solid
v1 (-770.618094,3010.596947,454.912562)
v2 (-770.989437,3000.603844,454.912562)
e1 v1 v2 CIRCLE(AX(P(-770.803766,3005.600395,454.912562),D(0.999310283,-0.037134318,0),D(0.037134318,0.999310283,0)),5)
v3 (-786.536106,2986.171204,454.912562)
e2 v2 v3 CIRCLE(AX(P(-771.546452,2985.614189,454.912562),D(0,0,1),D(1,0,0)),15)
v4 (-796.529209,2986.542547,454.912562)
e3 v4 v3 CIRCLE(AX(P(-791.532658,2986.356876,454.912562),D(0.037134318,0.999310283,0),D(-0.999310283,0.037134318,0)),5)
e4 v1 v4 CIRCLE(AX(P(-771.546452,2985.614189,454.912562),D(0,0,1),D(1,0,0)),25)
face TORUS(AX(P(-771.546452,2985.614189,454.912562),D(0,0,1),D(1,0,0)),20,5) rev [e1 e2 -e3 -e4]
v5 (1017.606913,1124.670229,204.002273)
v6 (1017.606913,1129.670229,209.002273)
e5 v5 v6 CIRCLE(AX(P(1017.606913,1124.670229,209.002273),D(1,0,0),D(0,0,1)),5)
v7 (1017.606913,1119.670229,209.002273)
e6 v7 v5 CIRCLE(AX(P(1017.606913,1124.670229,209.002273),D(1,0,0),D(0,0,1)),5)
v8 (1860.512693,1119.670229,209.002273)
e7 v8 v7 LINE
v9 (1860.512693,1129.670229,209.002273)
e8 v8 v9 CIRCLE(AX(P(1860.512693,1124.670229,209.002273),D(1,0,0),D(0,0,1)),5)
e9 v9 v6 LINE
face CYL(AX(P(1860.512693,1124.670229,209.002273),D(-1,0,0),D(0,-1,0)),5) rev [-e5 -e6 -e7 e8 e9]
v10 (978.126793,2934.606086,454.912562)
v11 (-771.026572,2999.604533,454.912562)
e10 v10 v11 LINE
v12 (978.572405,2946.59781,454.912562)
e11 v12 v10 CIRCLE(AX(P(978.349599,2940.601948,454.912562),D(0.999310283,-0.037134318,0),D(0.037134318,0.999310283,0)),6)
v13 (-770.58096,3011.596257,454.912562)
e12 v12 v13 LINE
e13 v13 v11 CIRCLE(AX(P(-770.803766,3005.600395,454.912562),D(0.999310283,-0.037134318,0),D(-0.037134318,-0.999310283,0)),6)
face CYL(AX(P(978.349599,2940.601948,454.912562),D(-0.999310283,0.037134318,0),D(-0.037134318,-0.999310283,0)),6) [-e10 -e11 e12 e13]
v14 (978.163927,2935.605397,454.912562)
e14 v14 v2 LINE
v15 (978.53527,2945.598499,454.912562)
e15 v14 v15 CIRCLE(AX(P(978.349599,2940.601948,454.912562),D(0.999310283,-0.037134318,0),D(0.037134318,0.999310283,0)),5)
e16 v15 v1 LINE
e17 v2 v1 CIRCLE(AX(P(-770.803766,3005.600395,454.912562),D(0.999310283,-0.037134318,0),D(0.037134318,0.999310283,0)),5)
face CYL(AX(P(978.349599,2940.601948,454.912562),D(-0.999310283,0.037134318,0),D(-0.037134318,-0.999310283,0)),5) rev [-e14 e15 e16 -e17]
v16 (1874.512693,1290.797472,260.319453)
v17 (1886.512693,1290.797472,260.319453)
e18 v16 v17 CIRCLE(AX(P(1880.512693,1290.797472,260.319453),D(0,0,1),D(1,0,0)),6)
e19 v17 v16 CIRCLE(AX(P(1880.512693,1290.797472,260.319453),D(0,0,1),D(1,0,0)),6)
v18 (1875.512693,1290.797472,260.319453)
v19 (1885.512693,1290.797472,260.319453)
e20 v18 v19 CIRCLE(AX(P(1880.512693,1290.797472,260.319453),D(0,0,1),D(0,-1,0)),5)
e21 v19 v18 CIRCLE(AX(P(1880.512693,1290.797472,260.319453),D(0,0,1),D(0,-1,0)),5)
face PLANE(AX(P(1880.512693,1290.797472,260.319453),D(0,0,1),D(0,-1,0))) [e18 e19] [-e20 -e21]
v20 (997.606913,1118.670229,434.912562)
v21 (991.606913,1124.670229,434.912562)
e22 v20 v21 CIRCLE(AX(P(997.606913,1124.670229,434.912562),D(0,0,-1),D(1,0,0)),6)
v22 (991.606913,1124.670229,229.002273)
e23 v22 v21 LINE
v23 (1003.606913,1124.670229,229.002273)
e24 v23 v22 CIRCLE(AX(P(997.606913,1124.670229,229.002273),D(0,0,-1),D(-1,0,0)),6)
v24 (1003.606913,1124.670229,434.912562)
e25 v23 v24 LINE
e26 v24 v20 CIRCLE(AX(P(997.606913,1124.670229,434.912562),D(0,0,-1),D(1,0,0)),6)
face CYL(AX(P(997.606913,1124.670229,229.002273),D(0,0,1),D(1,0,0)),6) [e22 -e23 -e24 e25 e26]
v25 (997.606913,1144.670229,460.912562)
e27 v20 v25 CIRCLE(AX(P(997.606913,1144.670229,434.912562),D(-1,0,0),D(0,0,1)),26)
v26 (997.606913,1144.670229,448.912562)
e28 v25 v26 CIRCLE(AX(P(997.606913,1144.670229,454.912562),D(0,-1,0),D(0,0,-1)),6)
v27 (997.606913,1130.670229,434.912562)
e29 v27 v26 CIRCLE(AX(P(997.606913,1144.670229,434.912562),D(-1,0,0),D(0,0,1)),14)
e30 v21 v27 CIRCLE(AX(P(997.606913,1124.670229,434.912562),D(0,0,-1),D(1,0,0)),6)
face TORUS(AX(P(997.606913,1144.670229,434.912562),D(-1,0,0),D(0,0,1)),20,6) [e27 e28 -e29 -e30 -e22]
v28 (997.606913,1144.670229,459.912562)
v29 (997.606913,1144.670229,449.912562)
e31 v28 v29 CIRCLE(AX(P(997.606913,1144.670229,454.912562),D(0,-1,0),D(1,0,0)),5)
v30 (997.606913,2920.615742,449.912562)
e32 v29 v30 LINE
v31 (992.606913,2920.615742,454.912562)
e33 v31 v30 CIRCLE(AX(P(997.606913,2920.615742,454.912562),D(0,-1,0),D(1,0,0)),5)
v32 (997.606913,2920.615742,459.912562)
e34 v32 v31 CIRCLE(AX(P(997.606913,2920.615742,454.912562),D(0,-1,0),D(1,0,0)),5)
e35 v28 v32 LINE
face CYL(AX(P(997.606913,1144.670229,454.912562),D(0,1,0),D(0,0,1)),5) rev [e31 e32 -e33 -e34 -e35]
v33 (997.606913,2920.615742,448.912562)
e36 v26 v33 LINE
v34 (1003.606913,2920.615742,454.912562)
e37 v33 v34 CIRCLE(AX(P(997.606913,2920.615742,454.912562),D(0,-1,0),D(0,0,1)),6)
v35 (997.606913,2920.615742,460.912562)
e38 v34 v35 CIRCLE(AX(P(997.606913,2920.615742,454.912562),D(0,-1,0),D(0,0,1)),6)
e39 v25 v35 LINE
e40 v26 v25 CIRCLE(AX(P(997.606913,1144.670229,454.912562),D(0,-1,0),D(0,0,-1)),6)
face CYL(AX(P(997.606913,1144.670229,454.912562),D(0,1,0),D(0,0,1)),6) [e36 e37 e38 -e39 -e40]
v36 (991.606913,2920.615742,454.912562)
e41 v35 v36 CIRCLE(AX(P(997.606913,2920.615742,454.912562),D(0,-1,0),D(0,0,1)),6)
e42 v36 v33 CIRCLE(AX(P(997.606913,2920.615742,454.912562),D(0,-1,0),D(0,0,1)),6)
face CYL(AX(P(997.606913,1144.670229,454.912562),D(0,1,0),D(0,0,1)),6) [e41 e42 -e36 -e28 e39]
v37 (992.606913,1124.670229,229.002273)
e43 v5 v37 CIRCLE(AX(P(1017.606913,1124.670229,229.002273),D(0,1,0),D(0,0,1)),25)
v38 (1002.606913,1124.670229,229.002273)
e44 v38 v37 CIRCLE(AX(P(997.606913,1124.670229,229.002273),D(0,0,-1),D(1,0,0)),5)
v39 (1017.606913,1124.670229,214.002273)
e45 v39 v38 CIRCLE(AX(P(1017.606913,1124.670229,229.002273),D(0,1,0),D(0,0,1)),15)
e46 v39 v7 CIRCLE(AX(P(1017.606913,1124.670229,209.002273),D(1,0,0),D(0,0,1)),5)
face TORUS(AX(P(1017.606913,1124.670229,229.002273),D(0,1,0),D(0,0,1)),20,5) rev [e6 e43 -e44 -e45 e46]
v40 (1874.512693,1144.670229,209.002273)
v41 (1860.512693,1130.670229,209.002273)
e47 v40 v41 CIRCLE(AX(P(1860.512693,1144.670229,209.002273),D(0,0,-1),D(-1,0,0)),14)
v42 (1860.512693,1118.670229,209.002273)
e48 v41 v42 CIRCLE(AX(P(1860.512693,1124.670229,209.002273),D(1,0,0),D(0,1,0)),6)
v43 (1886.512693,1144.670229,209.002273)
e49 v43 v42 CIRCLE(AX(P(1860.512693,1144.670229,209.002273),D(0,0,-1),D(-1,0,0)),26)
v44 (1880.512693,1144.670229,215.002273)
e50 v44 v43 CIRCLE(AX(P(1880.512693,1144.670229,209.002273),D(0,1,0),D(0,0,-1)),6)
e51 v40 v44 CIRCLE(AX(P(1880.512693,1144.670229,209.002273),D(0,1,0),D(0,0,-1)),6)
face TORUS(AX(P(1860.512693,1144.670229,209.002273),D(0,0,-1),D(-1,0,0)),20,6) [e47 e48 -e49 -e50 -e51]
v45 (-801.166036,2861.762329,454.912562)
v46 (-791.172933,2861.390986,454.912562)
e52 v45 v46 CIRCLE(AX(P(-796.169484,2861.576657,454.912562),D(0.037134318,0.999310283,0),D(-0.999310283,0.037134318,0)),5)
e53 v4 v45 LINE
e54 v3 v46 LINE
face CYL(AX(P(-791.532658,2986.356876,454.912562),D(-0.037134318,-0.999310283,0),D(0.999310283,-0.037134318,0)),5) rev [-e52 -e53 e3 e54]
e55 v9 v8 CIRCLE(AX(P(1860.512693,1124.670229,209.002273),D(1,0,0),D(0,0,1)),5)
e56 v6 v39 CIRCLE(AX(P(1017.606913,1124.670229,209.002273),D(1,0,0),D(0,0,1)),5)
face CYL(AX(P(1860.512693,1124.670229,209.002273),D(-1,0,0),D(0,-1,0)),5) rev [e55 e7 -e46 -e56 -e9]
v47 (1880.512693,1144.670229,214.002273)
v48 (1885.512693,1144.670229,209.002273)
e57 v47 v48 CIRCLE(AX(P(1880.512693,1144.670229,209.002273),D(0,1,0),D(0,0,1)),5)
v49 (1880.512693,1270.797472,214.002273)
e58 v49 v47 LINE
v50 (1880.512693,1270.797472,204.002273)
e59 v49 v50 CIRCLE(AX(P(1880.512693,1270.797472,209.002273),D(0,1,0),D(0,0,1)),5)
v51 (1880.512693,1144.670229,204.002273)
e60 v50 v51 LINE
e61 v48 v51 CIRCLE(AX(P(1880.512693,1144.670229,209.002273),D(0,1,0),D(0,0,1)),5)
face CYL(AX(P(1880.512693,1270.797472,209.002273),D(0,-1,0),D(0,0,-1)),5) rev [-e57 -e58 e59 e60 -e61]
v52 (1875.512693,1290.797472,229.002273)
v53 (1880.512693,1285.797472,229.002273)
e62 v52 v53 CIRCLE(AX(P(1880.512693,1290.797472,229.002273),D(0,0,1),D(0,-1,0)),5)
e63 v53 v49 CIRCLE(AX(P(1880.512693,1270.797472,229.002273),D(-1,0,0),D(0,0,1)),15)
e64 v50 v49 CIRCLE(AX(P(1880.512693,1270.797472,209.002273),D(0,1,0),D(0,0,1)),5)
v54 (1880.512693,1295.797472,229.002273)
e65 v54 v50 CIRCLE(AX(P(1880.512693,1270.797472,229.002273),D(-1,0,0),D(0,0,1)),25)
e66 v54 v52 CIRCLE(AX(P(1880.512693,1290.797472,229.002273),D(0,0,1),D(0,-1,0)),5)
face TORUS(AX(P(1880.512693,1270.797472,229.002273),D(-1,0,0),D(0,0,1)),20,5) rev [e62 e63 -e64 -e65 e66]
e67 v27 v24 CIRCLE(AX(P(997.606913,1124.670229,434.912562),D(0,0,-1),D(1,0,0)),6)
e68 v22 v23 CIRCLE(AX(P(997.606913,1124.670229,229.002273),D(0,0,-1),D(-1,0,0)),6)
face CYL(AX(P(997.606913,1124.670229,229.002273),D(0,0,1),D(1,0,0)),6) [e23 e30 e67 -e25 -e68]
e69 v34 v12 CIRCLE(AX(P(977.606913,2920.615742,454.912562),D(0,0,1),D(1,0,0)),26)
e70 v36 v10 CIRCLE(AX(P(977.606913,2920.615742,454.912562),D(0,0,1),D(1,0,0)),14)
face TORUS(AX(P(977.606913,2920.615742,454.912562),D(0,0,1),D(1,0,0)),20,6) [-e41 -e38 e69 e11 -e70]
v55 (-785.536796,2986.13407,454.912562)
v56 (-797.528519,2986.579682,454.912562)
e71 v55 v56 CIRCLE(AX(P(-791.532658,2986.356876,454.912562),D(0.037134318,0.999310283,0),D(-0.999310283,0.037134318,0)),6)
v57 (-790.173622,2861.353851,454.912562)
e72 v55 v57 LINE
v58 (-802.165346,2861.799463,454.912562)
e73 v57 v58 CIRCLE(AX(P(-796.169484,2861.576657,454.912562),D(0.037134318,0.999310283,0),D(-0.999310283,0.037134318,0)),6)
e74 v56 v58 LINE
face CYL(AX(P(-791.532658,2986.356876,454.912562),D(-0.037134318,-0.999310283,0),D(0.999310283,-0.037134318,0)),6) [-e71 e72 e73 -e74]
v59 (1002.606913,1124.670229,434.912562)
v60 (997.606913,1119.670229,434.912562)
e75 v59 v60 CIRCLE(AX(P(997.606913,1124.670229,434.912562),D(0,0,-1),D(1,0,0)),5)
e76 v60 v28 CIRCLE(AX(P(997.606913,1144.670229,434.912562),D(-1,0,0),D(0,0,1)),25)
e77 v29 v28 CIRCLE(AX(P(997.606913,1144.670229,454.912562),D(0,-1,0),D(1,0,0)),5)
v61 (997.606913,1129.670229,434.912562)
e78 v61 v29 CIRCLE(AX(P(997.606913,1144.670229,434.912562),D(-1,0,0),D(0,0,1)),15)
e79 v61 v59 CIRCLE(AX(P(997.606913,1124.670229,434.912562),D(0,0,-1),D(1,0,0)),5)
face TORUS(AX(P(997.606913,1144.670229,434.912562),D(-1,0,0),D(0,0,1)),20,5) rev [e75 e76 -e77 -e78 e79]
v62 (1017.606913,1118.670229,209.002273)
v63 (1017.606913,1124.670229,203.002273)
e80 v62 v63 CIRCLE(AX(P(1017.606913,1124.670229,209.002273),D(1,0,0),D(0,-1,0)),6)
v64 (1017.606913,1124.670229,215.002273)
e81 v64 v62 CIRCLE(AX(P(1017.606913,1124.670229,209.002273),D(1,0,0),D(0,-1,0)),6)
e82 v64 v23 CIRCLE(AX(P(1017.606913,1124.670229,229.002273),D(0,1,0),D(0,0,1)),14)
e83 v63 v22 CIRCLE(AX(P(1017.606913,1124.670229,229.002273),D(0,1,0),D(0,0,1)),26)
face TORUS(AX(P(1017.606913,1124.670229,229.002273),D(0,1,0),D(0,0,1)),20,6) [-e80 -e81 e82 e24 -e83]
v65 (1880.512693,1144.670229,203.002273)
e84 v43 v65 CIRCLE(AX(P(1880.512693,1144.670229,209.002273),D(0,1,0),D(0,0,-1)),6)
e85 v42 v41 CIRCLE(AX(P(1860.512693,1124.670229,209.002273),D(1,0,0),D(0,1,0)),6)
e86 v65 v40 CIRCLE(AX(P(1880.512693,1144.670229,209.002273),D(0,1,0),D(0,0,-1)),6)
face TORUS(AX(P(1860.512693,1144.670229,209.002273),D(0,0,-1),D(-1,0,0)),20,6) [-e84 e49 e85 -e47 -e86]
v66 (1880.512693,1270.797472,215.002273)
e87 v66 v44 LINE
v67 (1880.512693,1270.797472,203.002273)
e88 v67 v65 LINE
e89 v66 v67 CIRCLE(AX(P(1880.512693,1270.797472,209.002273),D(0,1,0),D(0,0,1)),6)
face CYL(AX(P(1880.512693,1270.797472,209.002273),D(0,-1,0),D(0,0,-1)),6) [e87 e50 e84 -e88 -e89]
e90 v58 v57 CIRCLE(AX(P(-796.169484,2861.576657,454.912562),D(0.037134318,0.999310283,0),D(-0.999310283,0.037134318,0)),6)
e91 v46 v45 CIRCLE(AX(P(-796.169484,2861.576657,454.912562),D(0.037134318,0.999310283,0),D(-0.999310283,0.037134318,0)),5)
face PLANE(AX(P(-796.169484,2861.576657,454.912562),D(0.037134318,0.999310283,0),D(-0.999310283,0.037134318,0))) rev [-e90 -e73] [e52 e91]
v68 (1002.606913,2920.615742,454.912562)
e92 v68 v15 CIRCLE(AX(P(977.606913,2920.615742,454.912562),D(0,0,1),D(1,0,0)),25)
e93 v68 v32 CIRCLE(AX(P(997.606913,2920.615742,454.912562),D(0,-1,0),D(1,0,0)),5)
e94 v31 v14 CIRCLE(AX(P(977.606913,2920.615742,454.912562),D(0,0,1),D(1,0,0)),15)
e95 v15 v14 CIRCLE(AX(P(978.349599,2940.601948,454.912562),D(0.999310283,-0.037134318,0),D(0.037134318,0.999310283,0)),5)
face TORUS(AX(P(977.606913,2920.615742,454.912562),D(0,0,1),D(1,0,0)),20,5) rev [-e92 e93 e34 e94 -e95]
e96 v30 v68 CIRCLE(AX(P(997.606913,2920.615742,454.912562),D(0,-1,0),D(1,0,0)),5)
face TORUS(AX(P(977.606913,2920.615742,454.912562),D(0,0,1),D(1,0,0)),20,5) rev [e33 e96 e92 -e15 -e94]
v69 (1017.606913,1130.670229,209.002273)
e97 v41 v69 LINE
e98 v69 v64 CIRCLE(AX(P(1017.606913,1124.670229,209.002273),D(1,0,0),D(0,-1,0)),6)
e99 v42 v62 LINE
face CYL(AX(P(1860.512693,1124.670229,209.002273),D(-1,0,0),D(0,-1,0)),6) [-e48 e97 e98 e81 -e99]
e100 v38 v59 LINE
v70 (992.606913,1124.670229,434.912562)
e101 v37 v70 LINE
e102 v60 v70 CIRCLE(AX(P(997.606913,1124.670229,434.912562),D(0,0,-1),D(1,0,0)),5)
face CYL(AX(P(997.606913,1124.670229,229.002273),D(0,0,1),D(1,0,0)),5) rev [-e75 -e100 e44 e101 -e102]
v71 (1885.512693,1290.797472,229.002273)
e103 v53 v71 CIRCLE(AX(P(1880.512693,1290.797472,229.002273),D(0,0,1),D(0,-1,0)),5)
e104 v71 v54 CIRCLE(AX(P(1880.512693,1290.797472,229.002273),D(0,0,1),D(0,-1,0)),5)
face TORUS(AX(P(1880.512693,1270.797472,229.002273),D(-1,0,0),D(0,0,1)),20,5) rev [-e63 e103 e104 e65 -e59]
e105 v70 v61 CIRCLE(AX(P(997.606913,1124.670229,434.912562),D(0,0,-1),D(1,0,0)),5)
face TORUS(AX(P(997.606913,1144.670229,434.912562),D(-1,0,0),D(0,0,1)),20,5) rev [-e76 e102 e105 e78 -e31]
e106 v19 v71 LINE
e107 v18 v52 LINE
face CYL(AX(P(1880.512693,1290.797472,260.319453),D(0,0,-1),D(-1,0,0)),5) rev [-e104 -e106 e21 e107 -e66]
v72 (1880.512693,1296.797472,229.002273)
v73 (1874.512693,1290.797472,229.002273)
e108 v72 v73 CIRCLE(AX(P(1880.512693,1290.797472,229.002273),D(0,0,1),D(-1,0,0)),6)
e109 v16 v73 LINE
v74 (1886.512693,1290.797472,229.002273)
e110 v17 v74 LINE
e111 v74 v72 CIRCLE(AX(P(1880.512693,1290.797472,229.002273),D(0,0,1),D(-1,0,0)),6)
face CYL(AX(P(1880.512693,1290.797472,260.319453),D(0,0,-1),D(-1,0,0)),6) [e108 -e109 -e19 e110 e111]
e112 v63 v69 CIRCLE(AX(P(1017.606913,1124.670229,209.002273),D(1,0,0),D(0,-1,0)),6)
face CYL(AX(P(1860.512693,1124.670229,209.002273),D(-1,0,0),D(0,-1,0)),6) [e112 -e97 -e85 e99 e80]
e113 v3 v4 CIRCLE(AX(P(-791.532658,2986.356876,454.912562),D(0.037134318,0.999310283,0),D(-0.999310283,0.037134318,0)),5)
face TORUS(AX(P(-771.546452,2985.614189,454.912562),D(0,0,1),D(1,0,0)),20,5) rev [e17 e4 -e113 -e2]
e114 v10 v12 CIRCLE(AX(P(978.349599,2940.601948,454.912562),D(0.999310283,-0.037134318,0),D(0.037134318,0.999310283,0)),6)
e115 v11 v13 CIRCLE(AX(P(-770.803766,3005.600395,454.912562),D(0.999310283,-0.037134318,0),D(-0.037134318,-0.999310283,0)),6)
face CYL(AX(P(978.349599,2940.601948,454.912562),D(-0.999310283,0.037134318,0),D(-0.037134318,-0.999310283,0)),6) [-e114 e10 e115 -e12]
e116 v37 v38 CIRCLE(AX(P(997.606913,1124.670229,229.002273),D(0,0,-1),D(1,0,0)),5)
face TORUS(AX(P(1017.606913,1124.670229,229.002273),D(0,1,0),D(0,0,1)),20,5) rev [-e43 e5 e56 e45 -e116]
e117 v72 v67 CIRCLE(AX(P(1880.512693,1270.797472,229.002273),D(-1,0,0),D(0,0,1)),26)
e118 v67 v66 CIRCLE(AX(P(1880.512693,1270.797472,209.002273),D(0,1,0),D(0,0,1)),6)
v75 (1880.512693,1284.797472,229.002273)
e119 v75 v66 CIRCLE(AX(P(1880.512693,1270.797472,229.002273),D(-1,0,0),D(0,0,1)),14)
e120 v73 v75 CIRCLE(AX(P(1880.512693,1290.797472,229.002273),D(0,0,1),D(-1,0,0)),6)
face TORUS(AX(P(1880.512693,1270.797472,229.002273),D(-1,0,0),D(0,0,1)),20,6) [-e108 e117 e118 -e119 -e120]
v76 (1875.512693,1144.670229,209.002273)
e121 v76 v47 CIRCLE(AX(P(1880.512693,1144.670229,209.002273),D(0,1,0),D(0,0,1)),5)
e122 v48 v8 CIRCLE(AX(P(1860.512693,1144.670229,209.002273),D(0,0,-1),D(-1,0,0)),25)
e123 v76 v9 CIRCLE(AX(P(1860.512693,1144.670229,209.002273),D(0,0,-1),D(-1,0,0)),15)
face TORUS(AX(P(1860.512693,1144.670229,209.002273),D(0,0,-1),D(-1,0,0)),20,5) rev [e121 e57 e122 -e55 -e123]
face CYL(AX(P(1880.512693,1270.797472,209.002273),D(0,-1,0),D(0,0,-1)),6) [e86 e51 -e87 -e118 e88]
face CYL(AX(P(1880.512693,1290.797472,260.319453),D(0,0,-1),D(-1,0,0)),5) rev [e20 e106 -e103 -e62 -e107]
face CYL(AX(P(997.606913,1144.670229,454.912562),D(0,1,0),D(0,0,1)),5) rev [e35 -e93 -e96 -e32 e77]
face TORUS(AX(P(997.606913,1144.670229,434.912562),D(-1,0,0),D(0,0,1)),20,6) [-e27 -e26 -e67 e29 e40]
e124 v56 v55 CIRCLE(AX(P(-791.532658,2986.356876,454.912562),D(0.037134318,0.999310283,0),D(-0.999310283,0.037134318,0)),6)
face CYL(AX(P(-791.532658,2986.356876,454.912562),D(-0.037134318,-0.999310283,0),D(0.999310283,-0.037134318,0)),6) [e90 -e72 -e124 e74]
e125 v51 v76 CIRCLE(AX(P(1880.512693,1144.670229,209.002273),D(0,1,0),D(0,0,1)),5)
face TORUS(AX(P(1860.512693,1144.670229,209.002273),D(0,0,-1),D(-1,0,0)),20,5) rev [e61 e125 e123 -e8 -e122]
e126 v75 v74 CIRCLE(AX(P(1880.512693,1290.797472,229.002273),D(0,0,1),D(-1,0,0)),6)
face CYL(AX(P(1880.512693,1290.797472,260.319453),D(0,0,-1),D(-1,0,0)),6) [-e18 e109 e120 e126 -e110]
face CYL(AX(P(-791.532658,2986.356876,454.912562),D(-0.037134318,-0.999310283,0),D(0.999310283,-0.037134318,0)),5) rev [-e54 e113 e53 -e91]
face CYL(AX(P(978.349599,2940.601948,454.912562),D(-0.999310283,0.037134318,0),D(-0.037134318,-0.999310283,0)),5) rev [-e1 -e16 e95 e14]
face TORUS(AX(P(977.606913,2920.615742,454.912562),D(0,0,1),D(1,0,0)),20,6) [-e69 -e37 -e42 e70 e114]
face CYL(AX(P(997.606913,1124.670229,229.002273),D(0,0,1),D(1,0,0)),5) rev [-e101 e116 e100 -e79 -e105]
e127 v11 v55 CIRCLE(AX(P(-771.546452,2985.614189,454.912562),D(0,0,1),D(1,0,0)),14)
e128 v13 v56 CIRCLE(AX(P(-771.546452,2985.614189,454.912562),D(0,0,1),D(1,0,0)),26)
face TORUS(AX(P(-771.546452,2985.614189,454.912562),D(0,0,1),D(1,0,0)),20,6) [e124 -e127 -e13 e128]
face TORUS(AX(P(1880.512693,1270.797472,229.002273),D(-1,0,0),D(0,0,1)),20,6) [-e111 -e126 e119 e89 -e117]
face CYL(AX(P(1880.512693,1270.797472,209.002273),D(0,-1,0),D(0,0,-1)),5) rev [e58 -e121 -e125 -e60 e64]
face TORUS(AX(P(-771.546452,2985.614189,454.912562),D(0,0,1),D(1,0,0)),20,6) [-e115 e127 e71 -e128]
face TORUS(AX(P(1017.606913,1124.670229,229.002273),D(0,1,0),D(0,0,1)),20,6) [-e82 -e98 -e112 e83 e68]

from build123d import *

# Parameters (mm, degrees)
SWEEP_1_PROFILE_R   = 6
SWEEP_1_PROFILE_R_2 = 5


with BuildPart() as part:
    # 扫描-薄件1: sweep along a curve in space
    with BuildLine() as sweep_1_path:
        Line((1880.512693362, 1290.797471808, 260.319452586), (1880.512693362, 1290.797471808, 229.002272719))
        ThreePointArc((1880.512693362, 1270.797471808, 209.002272719), (1880.512693362, 1284.939607432, 214.860137095), (1880.512693362, 1290.797471808, 229.002272719))
        Line((1880.512693362, 1270.797471808, 209.002272719), (1880.512693362, 1144.670229131, 209.002272719))
        ThreePointArc((1860.512693362, 1124.670229131, 209.002272719), (1874.654828986, 1130.528093508, 209.002272719), (1880.512693362, 1144.670229131, 209.002272719))
        Line((1860.512693362, 1124.670229131, 209.002272719), (1017.606912513, 1124.670229131, 209.002272719))
        ThreePointArc((997.606912513, 1124.670229131, 229.002272719), (1003.464776889, 1124.670229131, 214.860137095), (1017.606912513, 1124.670229131, 209.002272719))
        Line((997.606912513, 1124.670229131, 229.002272719), (997.606912513, 1124.670229131, 434.912562332))
        ThreePointArc((997.606912513, 1124.670229131, 434.912562332), (997.606912513, 1130.528093508, 449.054697956), (997.606912513, 1144.670229131, 454.912562332))
        Line((997.606912513, 1144.670229131, 454.912562332), (997.606912513, 2920.615742332, 454.912562332))
        ThreePointArc((997.606912513, 2920.615742332, 454.912562332), (992.009233976, 2934.492814663, 454.912562332), (978.349598866, 2940.601948, 454.912562332))
        Line((978.349598866, 2940.601948, 454.912562332), (-770.803765777, 3005.600395166, 454.912562332))
        ThreePointArc((-791.532657797, 2986.356875851, 454.912562332), (-785.153675131, 3000.271729612, 454.912562332), (-770.803765777, 3005.600395166, 454.912562332))
        Line((-791.532657797, 2986.356875851, 454.912562332), (-796.169484167, 2861.576657254, 454.912562332))
    # 扫描-薄件1 profile (on start of the path) → 扫描-薄件1 (sweep)
    with BuildSketch(Plane(origin=(1880.512693362, 1290.797471808, 260.319452586), x_dir=(-1, 0, 0), z_dir=(0, 0, -1))):
        Circle(SWEEP_1_PROFILE_R)
        Circle(SWEEP_1_PROFILE_R_2, mode=Mode.SUBTRACT)
    sweep(path=sweep_1_path.line)


solid = part.part
